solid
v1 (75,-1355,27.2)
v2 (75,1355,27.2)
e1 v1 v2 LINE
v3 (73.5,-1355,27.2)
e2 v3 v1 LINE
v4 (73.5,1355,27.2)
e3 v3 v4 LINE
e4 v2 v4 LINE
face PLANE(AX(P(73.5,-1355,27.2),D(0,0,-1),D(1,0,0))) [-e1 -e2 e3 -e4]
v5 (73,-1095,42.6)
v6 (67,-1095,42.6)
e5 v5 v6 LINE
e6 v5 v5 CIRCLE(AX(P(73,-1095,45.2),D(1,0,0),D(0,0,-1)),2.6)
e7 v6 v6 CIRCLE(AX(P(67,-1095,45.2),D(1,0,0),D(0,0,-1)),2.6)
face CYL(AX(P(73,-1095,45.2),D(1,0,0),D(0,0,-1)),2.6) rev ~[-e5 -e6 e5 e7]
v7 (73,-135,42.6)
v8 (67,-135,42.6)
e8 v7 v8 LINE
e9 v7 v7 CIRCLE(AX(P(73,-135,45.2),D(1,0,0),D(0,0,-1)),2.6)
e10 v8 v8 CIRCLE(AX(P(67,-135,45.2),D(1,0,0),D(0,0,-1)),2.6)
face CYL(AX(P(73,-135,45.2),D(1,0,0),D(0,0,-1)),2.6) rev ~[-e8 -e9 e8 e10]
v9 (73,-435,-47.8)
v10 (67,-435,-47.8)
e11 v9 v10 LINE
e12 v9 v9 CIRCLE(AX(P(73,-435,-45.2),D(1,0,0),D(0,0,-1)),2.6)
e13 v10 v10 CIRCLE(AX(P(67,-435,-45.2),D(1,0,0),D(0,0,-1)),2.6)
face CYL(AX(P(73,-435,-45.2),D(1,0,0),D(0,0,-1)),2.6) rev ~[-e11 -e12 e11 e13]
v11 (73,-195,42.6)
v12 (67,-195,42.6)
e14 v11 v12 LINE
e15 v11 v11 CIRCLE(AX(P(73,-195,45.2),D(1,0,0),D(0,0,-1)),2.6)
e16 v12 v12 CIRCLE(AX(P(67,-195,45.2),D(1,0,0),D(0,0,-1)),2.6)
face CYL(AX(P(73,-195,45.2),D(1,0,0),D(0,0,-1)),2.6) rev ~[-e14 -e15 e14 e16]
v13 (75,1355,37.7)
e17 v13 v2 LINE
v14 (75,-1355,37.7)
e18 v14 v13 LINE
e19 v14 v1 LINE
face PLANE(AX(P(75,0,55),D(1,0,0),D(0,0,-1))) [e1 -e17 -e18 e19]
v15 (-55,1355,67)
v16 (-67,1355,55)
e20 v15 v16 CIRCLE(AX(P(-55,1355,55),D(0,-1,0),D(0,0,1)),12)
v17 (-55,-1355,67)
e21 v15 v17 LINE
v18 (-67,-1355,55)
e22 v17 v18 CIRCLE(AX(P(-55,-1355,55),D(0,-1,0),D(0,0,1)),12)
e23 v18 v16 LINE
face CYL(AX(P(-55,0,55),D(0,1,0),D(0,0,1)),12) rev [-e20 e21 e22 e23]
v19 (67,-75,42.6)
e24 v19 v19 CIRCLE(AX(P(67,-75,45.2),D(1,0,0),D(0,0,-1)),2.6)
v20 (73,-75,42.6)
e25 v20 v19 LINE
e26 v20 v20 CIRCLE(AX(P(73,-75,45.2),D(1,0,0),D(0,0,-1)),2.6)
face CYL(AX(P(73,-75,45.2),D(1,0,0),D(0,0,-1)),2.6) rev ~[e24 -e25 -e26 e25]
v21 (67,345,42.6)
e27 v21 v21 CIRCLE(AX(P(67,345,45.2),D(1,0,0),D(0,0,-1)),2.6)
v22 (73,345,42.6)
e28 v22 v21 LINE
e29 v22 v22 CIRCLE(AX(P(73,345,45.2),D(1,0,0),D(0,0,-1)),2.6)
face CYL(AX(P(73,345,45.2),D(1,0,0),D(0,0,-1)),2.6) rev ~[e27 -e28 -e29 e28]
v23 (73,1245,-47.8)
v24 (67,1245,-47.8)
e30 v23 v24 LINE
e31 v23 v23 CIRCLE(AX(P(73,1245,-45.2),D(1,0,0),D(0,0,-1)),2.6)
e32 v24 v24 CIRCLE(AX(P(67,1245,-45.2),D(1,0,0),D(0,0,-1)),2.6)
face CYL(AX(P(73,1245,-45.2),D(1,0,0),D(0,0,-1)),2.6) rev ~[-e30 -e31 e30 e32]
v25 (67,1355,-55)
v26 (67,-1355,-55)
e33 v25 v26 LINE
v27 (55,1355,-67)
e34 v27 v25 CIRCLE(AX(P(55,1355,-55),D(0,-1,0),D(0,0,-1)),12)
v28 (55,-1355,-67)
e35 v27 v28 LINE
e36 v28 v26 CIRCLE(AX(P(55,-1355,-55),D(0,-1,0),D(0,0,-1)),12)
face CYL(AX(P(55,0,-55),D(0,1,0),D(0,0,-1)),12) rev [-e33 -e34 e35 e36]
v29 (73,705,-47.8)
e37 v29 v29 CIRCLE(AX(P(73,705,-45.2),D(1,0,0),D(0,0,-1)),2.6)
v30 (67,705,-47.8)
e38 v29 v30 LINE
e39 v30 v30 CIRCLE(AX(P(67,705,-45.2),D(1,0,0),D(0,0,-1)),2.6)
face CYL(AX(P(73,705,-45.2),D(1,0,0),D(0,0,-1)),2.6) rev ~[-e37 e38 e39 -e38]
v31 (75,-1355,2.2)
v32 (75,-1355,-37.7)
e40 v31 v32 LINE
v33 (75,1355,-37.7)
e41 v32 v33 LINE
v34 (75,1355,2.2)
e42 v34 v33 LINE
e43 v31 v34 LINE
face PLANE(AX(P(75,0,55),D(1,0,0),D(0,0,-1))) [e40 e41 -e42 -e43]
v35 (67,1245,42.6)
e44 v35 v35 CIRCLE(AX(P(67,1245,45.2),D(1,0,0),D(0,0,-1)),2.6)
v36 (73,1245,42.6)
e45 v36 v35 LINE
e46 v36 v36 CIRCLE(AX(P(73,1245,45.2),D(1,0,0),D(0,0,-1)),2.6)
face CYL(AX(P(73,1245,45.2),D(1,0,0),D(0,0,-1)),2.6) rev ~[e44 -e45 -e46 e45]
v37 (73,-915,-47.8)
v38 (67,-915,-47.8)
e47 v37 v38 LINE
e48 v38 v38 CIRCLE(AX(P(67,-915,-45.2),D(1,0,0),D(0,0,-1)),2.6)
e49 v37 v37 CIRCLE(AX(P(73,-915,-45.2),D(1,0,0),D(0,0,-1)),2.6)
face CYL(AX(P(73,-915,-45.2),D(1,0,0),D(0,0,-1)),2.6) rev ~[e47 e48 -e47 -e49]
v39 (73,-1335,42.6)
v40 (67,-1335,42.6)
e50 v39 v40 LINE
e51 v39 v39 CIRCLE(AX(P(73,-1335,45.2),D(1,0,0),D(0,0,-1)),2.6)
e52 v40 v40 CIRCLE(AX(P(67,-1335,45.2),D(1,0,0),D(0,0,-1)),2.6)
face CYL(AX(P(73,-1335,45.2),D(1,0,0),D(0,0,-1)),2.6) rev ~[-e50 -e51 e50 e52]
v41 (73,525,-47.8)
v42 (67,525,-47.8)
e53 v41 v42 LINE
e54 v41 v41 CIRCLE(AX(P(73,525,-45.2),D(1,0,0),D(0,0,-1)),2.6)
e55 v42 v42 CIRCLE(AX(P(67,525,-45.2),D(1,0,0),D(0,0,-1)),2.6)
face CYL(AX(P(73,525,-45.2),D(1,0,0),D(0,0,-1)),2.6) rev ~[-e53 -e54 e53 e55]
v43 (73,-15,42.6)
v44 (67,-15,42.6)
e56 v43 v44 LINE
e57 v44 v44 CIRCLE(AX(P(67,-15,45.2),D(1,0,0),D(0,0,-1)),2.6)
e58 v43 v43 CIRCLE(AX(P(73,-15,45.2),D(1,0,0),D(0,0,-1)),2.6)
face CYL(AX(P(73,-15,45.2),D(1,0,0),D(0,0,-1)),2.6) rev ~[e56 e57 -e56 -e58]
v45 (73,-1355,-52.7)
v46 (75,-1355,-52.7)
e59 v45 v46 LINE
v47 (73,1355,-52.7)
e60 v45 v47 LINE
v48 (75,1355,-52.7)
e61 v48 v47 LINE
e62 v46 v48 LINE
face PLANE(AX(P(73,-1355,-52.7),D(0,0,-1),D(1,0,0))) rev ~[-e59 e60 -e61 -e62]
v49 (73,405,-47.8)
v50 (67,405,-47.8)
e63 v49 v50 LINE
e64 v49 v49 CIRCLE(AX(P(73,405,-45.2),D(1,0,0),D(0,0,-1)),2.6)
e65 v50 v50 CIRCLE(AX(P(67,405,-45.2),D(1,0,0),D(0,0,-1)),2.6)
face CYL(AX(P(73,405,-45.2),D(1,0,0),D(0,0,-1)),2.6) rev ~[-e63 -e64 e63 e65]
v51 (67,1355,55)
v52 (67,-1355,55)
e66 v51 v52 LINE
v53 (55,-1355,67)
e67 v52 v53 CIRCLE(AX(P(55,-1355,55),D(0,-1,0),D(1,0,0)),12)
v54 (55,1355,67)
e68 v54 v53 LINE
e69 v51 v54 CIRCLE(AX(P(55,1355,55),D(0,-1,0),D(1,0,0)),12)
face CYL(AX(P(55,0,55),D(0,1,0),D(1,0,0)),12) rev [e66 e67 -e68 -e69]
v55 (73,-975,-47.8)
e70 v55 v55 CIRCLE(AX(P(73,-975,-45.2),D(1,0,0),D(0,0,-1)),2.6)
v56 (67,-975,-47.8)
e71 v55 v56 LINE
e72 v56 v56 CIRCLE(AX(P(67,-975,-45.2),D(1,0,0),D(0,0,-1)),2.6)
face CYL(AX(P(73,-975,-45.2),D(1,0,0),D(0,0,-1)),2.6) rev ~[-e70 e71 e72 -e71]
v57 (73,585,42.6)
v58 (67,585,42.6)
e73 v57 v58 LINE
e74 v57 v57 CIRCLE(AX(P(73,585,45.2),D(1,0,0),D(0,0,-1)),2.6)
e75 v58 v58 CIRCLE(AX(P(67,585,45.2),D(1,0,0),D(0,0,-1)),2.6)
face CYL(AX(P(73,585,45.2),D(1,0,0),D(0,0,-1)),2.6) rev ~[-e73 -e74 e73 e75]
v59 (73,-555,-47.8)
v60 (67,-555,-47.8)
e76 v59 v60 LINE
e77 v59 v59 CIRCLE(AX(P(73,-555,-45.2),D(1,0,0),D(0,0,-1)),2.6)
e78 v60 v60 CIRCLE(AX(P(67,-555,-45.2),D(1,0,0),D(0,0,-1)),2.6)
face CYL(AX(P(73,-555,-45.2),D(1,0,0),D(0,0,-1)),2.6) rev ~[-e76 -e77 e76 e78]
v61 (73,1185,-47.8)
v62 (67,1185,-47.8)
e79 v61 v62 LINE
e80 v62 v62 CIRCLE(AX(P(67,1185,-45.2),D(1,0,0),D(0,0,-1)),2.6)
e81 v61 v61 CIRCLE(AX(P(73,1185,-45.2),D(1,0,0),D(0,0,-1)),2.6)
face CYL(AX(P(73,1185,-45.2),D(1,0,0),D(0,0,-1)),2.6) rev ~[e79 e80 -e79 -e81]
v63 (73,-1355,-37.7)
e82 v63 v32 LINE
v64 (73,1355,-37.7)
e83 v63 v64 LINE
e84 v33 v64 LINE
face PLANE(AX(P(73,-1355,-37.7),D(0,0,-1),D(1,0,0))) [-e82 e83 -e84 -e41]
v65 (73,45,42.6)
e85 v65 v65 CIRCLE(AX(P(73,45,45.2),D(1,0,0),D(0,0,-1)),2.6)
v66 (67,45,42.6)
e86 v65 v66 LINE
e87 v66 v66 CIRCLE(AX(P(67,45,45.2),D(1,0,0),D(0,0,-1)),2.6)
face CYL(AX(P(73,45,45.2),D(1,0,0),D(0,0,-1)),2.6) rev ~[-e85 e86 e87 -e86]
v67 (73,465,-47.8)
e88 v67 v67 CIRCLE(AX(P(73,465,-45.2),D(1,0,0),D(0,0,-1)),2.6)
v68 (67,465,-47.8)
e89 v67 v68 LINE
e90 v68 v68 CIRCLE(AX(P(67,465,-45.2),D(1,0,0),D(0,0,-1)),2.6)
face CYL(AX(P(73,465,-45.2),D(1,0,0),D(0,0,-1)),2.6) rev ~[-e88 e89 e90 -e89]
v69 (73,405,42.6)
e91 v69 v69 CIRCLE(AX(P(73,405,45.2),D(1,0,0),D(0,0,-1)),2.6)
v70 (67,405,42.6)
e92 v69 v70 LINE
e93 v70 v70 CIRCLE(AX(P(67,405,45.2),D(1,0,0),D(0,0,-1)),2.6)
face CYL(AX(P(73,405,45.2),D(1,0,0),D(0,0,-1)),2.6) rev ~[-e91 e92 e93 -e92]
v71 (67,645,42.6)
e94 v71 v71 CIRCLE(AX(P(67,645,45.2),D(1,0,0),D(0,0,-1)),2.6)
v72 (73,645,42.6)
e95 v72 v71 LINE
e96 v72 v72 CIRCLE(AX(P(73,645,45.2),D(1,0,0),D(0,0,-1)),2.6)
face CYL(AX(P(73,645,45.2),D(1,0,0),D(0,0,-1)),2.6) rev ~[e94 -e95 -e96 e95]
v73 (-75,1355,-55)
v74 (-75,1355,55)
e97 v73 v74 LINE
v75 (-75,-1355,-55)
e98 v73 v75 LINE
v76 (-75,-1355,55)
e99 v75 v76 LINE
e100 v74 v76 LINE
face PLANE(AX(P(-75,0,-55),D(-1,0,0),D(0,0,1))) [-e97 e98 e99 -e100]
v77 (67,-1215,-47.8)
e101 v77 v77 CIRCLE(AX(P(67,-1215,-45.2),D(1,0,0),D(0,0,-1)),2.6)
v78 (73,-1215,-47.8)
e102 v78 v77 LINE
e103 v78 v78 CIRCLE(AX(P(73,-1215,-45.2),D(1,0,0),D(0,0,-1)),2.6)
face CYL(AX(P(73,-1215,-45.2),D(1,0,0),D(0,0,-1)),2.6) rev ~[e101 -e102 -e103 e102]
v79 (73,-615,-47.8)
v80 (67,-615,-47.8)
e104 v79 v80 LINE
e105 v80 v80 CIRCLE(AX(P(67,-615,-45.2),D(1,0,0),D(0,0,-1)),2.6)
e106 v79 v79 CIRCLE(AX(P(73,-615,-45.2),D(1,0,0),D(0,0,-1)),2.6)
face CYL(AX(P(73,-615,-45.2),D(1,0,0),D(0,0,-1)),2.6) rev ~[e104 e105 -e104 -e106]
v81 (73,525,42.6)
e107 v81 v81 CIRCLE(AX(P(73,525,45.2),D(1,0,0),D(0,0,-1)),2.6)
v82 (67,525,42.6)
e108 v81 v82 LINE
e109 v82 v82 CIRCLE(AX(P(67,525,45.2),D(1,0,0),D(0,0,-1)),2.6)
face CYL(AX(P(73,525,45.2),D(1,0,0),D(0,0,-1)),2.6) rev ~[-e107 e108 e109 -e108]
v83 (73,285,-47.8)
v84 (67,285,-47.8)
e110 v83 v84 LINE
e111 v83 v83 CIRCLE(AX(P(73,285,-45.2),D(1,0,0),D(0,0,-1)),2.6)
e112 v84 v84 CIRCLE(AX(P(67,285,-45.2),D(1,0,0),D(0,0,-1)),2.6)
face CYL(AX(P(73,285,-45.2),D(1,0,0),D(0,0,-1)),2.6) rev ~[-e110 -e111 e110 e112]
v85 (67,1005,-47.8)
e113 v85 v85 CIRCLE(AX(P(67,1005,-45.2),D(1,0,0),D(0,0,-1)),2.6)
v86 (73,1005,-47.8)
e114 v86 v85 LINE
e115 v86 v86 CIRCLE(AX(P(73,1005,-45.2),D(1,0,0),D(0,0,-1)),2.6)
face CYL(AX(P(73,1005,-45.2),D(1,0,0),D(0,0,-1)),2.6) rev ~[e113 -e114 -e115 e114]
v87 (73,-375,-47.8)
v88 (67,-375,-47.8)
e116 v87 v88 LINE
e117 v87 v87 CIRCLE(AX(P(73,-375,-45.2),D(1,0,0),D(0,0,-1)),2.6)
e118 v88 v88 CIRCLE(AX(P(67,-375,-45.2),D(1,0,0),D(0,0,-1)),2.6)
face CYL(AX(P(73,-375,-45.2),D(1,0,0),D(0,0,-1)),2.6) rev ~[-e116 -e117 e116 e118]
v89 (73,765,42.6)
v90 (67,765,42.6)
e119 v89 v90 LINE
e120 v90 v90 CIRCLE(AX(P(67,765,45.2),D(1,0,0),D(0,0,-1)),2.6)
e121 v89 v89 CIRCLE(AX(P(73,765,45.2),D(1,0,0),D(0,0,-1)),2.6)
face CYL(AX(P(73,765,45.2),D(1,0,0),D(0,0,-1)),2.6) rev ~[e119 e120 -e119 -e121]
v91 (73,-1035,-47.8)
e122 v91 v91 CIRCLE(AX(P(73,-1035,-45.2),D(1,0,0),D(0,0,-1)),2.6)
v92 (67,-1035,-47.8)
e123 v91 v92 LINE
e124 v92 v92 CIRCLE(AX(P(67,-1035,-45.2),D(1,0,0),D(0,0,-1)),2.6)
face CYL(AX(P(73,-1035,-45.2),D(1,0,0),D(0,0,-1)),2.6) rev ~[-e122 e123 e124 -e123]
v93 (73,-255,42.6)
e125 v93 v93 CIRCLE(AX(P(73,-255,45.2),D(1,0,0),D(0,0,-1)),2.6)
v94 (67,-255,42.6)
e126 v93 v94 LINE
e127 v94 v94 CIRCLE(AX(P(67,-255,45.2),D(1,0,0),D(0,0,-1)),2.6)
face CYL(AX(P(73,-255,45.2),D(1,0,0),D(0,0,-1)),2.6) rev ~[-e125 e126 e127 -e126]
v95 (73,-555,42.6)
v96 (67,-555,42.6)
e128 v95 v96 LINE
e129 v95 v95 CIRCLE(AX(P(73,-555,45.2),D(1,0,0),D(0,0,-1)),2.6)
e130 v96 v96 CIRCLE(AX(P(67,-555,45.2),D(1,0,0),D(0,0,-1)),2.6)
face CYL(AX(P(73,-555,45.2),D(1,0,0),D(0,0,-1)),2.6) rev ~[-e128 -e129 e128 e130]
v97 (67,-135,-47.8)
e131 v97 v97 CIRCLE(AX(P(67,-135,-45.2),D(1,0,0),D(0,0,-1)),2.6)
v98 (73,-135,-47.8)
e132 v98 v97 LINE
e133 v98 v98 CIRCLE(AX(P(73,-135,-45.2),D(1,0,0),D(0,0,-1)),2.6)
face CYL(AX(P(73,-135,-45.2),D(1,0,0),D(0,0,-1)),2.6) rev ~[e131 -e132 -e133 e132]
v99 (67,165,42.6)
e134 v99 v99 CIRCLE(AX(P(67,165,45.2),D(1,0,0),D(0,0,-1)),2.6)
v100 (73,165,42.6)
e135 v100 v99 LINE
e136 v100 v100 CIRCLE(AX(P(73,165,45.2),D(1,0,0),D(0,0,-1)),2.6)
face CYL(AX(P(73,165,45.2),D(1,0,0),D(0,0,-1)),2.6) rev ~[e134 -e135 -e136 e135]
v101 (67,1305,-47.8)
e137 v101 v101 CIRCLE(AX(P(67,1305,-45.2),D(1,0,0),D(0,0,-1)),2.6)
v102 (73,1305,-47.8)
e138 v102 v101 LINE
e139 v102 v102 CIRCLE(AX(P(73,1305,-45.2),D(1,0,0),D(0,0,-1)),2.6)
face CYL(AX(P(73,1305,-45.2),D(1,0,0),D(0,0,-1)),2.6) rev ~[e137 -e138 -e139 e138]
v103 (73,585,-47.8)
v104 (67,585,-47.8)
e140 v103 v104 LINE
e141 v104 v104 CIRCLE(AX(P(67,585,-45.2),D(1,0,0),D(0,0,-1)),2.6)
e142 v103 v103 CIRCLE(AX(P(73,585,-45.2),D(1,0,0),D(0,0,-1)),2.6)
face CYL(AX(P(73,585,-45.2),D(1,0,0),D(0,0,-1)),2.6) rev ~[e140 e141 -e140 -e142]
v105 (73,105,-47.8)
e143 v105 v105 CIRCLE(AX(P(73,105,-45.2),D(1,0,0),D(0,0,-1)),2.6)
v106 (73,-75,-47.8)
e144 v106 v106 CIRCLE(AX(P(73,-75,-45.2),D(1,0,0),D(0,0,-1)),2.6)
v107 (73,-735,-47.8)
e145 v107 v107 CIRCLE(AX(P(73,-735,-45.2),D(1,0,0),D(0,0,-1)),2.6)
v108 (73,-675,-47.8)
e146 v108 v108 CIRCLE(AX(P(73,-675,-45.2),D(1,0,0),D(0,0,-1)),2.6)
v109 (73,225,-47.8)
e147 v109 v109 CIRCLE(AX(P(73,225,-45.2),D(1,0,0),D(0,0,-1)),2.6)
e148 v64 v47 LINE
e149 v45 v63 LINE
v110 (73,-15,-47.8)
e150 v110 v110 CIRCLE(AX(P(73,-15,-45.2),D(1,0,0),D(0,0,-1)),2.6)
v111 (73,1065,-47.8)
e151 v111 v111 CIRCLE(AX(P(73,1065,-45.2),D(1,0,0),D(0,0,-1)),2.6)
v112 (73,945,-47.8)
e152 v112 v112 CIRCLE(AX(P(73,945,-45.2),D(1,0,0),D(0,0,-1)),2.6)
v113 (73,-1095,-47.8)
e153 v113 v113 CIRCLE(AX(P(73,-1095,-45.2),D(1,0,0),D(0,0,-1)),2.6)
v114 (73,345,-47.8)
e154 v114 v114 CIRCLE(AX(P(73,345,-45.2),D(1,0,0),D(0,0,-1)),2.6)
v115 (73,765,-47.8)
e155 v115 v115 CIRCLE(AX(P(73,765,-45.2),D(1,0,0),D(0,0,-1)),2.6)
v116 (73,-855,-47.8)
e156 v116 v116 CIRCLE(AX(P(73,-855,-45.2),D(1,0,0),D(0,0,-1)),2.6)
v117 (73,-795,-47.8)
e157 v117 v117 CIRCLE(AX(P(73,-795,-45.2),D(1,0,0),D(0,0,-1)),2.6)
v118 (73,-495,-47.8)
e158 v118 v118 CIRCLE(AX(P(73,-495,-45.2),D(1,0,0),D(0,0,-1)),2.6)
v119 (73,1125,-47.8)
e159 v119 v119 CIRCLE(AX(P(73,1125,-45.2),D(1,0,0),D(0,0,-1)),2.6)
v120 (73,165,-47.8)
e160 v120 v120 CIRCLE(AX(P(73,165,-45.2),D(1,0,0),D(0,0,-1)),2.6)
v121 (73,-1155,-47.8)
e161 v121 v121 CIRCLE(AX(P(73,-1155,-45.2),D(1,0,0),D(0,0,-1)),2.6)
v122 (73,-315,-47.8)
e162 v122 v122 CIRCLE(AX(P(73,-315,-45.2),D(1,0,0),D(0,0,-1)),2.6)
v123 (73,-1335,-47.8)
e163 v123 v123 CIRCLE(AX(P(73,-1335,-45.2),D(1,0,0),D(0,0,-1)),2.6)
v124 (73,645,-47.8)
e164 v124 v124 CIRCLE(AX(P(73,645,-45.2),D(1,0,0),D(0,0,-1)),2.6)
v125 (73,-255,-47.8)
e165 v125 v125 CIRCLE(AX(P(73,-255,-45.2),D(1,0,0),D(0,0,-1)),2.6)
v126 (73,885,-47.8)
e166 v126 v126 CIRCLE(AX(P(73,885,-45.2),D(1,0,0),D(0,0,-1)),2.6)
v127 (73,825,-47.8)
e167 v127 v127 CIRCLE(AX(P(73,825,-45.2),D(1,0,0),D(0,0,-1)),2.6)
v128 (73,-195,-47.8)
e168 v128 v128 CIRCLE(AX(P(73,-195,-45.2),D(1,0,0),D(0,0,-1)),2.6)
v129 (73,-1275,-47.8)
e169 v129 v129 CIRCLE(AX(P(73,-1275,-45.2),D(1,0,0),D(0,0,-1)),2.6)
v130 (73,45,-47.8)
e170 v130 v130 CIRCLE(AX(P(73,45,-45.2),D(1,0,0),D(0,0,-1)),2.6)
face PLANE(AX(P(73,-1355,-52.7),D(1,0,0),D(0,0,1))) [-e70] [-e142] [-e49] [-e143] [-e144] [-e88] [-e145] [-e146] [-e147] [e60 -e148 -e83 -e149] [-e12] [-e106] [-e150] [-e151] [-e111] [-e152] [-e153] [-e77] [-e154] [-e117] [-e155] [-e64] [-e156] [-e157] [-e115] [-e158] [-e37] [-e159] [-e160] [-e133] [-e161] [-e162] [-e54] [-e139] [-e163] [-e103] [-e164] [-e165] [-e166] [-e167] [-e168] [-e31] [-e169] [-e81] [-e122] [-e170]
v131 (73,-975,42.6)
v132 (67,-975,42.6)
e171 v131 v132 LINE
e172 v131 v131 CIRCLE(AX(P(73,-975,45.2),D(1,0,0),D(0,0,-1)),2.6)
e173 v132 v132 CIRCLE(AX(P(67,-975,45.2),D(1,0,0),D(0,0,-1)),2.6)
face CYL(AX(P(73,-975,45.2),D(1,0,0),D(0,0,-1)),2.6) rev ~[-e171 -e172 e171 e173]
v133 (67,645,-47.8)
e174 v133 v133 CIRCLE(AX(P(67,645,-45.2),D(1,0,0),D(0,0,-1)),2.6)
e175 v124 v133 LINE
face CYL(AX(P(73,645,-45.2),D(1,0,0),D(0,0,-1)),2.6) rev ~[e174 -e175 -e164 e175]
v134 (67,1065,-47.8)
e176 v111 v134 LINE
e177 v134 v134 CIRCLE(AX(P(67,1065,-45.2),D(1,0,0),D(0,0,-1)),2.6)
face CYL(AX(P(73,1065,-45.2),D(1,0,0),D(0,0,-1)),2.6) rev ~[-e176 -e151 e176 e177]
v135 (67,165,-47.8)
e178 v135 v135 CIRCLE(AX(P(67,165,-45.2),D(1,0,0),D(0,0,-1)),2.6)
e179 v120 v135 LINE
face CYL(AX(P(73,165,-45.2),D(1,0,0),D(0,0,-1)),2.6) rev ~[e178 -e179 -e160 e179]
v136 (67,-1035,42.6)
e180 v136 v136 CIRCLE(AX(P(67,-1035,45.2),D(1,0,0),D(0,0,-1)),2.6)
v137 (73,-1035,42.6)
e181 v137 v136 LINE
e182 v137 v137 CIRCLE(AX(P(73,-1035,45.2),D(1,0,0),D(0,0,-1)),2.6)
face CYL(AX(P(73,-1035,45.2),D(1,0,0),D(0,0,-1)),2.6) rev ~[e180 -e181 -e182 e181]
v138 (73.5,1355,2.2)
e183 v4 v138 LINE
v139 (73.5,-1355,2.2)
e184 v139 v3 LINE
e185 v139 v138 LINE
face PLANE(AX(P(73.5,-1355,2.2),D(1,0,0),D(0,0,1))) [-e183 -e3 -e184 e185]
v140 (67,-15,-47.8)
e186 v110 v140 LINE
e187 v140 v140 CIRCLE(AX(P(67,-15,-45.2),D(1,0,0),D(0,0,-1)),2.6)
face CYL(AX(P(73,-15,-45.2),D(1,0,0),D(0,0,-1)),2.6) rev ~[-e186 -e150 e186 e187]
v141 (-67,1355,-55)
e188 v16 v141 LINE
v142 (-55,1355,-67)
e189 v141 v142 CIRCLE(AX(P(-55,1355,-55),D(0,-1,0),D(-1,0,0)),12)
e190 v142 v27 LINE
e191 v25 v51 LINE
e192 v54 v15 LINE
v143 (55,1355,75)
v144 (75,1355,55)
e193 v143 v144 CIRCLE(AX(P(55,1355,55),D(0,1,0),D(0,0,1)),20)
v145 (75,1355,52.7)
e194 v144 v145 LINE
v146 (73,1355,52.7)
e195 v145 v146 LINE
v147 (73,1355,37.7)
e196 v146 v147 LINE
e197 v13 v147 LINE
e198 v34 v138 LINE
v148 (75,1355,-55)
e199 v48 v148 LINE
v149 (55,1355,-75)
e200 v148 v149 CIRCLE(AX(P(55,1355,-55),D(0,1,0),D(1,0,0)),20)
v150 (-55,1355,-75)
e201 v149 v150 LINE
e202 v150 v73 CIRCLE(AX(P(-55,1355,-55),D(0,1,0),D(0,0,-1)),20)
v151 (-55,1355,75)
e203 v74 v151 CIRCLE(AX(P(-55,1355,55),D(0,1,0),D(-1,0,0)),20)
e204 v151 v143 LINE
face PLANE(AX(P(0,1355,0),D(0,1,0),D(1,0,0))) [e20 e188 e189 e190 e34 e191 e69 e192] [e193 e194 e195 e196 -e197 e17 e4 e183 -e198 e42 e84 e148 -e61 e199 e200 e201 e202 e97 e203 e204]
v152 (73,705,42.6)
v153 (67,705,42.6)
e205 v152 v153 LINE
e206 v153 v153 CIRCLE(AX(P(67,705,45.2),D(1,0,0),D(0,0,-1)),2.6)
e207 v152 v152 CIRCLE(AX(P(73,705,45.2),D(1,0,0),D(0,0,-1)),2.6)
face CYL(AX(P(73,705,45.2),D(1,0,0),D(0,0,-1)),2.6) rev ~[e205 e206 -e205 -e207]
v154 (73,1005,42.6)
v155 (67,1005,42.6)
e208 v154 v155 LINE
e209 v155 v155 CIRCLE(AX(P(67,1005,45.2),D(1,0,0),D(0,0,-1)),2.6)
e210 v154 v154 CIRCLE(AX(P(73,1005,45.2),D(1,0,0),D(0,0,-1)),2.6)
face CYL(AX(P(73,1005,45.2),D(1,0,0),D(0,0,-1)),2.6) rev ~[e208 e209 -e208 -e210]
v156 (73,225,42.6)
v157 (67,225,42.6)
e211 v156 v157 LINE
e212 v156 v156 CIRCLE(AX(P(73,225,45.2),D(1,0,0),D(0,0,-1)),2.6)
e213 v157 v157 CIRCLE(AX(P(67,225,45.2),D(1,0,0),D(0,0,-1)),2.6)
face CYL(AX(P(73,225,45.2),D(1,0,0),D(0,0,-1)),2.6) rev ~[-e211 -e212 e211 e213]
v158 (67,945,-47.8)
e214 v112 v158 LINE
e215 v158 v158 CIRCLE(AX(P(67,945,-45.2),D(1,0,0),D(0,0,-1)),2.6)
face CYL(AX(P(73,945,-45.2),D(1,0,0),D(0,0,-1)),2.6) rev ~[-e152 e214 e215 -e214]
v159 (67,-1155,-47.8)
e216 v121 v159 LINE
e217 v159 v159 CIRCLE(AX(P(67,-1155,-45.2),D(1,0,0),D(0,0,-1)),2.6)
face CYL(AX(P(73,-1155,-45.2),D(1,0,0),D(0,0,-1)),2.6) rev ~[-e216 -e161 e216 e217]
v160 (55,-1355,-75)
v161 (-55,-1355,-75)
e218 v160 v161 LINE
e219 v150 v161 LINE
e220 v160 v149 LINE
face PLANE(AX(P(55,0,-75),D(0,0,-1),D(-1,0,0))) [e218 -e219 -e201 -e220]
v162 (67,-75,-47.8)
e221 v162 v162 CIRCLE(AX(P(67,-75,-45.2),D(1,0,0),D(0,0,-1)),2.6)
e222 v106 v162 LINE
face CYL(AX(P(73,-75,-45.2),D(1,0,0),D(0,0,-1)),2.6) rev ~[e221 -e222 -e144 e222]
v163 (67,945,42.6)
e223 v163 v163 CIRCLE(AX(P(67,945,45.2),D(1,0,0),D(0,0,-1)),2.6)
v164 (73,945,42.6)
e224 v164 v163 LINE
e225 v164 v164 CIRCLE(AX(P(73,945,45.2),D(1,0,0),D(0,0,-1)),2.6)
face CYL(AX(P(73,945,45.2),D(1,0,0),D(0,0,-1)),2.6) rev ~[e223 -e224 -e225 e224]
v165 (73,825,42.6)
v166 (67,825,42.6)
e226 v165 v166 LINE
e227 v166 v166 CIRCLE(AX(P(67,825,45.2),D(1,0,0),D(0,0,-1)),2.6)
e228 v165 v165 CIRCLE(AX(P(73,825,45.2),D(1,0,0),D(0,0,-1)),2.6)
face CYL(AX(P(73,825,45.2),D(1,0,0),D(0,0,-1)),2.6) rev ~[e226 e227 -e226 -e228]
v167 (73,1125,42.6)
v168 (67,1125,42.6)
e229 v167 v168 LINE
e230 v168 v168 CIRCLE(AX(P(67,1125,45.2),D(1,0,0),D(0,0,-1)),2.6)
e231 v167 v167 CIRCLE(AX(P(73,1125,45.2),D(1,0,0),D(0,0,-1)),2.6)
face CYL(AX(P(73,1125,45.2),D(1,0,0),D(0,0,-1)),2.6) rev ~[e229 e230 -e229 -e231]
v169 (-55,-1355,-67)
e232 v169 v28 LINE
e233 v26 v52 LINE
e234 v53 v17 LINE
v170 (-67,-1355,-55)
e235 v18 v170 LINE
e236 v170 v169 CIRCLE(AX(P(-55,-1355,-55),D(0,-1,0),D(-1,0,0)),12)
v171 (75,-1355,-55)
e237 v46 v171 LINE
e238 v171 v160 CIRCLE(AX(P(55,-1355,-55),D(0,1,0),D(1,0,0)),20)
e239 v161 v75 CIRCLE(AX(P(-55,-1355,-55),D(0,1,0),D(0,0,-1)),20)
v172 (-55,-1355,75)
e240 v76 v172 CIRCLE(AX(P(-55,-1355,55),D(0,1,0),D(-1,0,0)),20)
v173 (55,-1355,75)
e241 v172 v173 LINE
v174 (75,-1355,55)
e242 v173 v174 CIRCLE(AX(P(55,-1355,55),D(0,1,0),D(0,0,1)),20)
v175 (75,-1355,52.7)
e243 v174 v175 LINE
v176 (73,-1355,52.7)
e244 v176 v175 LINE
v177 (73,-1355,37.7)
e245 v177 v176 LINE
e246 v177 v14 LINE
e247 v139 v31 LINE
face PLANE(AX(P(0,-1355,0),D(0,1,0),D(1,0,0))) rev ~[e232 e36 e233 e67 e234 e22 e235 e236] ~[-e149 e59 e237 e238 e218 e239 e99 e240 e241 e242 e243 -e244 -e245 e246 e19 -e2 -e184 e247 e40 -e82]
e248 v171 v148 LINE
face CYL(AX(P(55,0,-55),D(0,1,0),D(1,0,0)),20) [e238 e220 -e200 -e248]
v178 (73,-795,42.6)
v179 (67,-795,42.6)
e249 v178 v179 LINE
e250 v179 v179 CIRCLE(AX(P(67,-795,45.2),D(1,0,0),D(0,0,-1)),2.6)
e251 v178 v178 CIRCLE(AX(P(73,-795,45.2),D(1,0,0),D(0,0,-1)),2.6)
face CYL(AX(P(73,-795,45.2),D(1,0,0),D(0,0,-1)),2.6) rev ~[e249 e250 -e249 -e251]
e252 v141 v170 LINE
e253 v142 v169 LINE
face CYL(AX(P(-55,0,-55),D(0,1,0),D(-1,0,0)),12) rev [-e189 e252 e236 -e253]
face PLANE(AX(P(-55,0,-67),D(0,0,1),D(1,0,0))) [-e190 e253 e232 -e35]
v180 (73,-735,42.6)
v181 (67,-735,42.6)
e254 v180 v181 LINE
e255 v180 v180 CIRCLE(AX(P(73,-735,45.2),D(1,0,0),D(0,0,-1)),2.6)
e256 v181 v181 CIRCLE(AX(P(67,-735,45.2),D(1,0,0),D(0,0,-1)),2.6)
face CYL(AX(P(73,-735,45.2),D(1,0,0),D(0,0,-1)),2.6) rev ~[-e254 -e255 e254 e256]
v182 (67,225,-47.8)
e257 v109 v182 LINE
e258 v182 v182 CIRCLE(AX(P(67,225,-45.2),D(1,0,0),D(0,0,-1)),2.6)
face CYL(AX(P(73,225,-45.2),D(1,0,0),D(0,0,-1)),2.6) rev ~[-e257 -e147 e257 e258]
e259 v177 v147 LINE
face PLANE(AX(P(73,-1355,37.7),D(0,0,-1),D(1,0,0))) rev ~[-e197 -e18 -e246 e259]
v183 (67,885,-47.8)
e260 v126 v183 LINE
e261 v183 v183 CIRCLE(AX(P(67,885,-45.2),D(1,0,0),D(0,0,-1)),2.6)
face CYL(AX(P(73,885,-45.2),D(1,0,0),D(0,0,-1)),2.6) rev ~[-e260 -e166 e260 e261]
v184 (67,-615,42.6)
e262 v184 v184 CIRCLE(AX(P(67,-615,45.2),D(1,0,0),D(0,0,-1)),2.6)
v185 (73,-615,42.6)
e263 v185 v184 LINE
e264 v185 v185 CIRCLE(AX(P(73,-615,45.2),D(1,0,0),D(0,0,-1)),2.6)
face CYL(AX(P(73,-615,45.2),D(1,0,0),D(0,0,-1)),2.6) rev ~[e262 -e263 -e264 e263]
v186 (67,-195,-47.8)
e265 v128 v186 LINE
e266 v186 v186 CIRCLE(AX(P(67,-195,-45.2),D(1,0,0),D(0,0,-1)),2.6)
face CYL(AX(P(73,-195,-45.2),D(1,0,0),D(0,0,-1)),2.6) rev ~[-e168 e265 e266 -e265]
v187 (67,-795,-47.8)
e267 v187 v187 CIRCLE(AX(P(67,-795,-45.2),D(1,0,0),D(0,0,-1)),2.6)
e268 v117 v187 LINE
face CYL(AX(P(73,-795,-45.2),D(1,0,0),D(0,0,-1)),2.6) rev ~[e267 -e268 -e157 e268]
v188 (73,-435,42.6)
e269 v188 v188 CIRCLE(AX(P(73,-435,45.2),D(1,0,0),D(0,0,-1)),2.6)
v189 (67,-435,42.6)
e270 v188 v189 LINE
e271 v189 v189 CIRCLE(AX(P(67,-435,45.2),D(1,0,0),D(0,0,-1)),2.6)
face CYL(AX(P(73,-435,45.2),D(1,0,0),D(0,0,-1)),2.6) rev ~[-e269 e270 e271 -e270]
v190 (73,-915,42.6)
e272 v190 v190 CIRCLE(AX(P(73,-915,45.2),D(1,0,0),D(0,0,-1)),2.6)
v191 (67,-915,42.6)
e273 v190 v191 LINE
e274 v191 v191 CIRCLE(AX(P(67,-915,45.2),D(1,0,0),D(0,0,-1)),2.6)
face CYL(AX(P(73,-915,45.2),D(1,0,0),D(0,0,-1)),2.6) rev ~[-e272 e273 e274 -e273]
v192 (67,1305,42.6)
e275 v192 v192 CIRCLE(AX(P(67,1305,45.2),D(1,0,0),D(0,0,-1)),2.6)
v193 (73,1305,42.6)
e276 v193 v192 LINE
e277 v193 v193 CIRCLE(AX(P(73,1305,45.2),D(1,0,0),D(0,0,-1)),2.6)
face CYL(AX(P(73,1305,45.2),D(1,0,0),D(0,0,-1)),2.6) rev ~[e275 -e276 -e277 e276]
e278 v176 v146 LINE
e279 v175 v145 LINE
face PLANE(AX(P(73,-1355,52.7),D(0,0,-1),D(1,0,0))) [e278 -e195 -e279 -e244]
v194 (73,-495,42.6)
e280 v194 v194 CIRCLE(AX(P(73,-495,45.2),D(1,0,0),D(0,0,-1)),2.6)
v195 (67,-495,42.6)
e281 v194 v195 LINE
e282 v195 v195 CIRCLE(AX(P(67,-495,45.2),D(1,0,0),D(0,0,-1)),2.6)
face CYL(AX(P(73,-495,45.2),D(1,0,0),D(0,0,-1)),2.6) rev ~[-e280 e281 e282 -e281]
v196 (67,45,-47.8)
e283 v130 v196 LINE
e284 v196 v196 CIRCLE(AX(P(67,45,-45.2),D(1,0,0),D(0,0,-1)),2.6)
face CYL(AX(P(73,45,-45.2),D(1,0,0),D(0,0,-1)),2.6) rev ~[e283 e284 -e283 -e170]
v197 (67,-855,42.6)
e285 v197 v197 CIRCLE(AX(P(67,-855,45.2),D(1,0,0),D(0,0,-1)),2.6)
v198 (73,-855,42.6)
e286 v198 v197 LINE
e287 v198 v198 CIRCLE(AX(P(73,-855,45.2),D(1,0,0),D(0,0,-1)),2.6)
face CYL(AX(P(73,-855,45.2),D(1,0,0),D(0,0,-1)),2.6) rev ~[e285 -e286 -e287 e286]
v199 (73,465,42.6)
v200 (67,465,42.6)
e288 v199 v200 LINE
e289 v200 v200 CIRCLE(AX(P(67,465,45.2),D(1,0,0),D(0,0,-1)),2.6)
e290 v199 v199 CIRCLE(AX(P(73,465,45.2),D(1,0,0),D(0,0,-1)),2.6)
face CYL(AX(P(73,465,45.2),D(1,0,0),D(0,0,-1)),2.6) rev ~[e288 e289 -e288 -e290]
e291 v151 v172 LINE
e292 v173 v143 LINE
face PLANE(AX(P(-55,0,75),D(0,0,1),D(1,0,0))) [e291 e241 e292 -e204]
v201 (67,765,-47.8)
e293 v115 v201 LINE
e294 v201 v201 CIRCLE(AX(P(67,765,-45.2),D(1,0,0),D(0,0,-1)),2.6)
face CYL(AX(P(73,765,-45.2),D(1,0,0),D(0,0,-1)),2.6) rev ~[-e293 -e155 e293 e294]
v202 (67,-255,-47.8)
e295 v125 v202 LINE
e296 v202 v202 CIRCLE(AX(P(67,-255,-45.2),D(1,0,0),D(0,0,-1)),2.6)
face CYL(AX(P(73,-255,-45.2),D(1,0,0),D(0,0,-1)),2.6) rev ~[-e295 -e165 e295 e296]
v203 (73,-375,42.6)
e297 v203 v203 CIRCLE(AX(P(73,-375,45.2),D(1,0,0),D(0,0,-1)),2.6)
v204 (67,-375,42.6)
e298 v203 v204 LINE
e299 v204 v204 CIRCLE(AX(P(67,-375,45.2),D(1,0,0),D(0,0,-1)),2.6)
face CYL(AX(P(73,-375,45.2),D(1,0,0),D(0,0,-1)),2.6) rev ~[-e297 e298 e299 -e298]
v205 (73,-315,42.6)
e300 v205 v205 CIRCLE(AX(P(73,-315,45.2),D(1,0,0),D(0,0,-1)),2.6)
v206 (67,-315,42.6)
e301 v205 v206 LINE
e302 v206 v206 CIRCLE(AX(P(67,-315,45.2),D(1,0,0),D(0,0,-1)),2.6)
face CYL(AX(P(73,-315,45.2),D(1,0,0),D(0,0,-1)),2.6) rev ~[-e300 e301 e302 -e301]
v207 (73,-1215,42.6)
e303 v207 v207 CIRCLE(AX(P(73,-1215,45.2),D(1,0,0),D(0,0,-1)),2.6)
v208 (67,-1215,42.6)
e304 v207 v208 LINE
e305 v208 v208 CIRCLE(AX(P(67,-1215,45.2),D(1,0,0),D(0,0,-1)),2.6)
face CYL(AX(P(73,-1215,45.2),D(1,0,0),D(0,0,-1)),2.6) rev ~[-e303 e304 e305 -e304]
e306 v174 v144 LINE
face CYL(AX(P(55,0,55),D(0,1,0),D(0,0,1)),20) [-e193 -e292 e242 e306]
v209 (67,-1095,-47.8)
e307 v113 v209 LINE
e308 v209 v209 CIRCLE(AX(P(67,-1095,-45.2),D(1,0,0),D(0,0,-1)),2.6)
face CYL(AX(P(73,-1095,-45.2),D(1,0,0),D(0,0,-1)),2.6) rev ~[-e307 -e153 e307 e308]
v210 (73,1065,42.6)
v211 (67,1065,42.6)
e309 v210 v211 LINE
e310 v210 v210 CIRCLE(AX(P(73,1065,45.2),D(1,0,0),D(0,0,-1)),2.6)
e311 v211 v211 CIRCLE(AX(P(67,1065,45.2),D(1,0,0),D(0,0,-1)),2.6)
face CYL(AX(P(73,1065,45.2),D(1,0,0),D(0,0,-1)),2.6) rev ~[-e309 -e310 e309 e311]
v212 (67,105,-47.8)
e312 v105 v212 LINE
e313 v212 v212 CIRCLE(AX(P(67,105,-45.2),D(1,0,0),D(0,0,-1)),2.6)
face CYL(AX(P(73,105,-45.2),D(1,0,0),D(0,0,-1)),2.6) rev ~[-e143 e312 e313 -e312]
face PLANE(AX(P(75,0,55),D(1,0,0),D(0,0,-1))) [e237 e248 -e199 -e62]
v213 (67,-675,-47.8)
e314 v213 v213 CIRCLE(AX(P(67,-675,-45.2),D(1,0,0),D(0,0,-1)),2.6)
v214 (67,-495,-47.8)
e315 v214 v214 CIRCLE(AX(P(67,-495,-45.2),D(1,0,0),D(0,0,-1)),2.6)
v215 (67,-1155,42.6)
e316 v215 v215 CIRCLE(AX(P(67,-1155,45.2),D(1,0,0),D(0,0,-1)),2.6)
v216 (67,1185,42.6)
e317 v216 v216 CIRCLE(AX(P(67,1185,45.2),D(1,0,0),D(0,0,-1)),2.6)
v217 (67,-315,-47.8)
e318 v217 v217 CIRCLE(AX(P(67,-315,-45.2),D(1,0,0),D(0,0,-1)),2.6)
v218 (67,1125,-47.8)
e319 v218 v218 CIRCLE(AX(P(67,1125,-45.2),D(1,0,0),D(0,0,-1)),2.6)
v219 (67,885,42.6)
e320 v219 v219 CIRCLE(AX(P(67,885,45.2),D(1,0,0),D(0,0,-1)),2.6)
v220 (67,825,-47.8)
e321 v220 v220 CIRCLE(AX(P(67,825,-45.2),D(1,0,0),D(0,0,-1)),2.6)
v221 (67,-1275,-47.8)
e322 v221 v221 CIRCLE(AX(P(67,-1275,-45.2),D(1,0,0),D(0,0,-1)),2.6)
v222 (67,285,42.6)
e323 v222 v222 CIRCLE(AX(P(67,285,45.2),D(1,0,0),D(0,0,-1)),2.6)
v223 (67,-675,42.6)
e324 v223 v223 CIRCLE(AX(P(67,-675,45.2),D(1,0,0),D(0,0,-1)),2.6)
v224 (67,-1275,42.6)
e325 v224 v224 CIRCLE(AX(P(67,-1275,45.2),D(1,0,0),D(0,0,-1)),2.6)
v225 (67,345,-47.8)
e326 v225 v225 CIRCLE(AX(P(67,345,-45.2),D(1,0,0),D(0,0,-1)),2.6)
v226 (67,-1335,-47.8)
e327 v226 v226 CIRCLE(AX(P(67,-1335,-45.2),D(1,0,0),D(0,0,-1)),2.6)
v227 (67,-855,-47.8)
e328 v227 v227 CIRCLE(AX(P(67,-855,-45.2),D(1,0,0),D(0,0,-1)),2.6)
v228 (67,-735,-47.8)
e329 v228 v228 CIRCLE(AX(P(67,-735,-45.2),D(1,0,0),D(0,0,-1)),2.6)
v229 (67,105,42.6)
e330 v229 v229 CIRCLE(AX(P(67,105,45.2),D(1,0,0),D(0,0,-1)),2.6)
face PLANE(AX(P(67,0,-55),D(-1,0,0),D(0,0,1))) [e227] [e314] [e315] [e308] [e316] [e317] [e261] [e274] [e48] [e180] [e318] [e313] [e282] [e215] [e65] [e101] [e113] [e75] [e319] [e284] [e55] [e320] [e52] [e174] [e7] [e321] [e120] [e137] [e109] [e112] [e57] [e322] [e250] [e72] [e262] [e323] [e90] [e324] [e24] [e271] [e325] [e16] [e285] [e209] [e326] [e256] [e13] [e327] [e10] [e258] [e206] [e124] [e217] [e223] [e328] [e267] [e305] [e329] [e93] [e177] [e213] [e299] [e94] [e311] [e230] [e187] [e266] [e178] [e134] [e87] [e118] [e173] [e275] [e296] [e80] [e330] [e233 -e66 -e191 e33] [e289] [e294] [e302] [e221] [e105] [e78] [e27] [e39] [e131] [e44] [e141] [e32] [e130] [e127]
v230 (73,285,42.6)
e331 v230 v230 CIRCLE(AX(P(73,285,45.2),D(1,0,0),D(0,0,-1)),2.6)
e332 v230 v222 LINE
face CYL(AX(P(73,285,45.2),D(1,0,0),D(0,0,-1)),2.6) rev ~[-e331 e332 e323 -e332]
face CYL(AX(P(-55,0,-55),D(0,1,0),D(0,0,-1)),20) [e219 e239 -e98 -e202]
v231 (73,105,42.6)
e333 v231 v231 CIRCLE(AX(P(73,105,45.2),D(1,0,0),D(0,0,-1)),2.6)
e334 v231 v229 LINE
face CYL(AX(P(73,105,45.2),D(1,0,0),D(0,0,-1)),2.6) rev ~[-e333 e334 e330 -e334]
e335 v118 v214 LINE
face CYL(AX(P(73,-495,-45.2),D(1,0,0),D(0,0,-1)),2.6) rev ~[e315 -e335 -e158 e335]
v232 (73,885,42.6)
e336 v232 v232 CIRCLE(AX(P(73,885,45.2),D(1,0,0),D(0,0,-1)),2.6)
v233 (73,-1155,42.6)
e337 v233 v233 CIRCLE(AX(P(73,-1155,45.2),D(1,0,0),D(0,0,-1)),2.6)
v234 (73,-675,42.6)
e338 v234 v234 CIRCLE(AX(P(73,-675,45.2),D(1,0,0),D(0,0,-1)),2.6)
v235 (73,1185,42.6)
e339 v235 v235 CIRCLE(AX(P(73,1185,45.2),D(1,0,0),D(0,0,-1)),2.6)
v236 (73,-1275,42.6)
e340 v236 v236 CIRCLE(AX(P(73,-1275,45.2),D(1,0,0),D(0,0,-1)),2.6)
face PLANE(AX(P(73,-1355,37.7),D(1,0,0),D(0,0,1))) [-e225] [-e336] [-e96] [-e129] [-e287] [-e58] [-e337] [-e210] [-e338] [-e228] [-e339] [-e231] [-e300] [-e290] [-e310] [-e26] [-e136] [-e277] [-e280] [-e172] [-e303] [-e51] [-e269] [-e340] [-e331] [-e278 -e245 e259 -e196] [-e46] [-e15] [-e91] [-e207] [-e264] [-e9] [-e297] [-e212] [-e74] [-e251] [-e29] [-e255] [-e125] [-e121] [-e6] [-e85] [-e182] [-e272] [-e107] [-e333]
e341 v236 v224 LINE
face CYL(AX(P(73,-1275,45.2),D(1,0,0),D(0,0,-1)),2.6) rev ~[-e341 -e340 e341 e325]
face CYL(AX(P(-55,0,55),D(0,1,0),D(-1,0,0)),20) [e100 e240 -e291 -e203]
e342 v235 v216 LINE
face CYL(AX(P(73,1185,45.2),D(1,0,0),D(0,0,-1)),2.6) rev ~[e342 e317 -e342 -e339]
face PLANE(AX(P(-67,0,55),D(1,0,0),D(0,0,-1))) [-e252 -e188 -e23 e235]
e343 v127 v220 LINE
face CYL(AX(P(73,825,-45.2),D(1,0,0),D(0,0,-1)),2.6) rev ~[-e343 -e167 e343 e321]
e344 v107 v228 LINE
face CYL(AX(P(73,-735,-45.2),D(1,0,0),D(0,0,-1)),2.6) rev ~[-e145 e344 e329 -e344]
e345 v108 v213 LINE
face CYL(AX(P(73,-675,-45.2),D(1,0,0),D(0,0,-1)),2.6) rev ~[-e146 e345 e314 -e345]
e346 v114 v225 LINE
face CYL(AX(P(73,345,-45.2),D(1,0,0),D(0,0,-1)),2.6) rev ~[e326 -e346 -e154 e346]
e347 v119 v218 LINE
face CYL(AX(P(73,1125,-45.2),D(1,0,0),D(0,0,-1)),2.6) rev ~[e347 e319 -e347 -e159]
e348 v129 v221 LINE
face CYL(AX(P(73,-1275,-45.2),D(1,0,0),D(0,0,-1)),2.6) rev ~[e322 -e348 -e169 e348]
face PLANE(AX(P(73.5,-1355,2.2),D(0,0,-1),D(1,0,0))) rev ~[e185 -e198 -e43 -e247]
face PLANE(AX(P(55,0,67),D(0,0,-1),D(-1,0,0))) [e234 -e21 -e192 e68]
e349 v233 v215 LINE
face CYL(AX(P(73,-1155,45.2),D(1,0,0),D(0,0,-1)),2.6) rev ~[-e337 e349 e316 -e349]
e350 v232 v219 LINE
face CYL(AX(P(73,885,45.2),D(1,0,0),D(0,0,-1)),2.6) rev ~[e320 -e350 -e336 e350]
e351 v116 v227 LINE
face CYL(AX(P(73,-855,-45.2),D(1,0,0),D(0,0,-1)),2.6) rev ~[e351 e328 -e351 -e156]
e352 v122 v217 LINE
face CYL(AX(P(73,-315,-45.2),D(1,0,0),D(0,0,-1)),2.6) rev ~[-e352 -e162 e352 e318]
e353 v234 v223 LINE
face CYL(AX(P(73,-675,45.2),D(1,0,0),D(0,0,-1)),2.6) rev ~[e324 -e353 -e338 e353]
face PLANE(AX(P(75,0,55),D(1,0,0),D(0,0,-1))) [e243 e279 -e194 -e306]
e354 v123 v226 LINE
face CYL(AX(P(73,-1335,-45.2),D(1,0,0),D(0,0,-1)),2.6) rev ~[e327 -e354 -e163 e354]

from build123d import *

# Parameters (mm, degrees)
BOSS_EXTRUDE1_DEPTH  = 1355
SKETCH2_W            = 2
SKETCH2_H            = 15
SKETCH2_W_2          = 1.5
SKETCH2_H_2          = 25
CUT_EXTRUDE1_DEPTH   = 4000
CUT_EXTRUDE2_REACH   = 1367.121
SKETCH4_R            = 2.6
LPATTERN2_COUNT      = 2
LPATTERN2_PITCH      = 90.4
LPATTERN2_COUNT_DIR2 = 45
LPATTERN2_PITCH_DIR2 = 60


with BuildPart() as part:
    # Sketch1 → Boss-Extrude1 (new, symmetric)
    with BuildSketch(Plane(origin=(0, 0, 0), x_dir=(1, 0, 0), z_dir=(0, 1, 0))):
        with BuildLine():
            Line((-55, -75), (55, -75))
            ThreePointArc((55, -75), (69.142135624, -69.142135624), (75, -55))
            Line((75, -55), (75, 55))
            ThreePointArc((75, 55), (69.142135624, 69.142135624), (55, 75))
            Line((55, 75), (-55, 75))
            ThreePointArc((-55, 75), (-69.142135624, 69.142135624), (-75, 55))
            Line((-75, 55), (-75, -55))
            ThreePointArc((-75, -55), (-69.142135624, -69.142135624), (-55, -75))
        make_face()
        with BuildLine():
            Line((-67, -55), (-67, 55))
            ThreePointArc((-67, 55), (-63.485281374, 63.485281374), (-55, 67))
            Line((-55, 67), (55, 67))
            ThreePointArc((55, 67), (63.485281374, 63.485281374), (67, 55))
            Line((67, 55), (67, -55))
            ThreePointArc((67, -55), (63.485281374, -63.485281374), (55, -67))
            Line((55, -67), (-55, -67))
            ThreePointArc((-55, -67), (-63.485281374, -63.485281374), (-67, -55))
        make_face(mode=Mode.SUBTRACT)
    extrude(amount=BOSS_EXTRUDE1_DEPTH, both=True)

    # Sketch2 → Cut-Extrude1 (cut)
    with BuildSketch(Plane.XZ.offset(1355)):
        with Locations((74, 45.2)):
            Rectangle(SKETCH2_W, SKETCH2_H)
        with Locations((74, -45.2)):
            Rectangle(SKETCH2_W, SKETCH2_H)
        with Locations((74.25, 14.7)):
            Rectangle(SKETCH2_W_2, SKETCH2_H_2)
    extrude(amount=-CUT_EXTRUDE1_DEPTH, mode=Mode.SUBTRACT)

    # Sketch4 → Cut-Extrude2 (cut, up to next)
    with BuildSketch(Plane(origin=(73, 0, 0), x_dir=(0, 0, -1), z_dir=(1, 0, 0)), mode=Mode.PRIVATE) as cut_extrude2_sk1:
        with Locations((-45.2, -1335)):
            Circle(SKETCH4_R)
    cut_extrude2_tool1 = extrude(cut_extrude2_sk1.sketch, amount=-CUT_EXTRUDE2_REACH, mode=Mode.PRIVATE) & part.part
    cut_extrude2 = cut_extrude2_tool1.solids().sort_by_distance((73, -1335, 45.2))[0]
    add(cut_extrude2, mode=Mode.SUBTRACT)

    # LPattern2: Cut-Extrude2 2 × 45
    with Locations(*[(0, j * LPATTERN2_PITCH_DIR2, -i * LPATTERN2_PITCH) for i in range(LPATTERN2_COUNT) for j in range(LPATTERN2_COUNT_DIR2) if (i, j) != (0, 0)]):
        add(cut_extrude2, mode=Mode.SUBTRACT)


solid = part.part
